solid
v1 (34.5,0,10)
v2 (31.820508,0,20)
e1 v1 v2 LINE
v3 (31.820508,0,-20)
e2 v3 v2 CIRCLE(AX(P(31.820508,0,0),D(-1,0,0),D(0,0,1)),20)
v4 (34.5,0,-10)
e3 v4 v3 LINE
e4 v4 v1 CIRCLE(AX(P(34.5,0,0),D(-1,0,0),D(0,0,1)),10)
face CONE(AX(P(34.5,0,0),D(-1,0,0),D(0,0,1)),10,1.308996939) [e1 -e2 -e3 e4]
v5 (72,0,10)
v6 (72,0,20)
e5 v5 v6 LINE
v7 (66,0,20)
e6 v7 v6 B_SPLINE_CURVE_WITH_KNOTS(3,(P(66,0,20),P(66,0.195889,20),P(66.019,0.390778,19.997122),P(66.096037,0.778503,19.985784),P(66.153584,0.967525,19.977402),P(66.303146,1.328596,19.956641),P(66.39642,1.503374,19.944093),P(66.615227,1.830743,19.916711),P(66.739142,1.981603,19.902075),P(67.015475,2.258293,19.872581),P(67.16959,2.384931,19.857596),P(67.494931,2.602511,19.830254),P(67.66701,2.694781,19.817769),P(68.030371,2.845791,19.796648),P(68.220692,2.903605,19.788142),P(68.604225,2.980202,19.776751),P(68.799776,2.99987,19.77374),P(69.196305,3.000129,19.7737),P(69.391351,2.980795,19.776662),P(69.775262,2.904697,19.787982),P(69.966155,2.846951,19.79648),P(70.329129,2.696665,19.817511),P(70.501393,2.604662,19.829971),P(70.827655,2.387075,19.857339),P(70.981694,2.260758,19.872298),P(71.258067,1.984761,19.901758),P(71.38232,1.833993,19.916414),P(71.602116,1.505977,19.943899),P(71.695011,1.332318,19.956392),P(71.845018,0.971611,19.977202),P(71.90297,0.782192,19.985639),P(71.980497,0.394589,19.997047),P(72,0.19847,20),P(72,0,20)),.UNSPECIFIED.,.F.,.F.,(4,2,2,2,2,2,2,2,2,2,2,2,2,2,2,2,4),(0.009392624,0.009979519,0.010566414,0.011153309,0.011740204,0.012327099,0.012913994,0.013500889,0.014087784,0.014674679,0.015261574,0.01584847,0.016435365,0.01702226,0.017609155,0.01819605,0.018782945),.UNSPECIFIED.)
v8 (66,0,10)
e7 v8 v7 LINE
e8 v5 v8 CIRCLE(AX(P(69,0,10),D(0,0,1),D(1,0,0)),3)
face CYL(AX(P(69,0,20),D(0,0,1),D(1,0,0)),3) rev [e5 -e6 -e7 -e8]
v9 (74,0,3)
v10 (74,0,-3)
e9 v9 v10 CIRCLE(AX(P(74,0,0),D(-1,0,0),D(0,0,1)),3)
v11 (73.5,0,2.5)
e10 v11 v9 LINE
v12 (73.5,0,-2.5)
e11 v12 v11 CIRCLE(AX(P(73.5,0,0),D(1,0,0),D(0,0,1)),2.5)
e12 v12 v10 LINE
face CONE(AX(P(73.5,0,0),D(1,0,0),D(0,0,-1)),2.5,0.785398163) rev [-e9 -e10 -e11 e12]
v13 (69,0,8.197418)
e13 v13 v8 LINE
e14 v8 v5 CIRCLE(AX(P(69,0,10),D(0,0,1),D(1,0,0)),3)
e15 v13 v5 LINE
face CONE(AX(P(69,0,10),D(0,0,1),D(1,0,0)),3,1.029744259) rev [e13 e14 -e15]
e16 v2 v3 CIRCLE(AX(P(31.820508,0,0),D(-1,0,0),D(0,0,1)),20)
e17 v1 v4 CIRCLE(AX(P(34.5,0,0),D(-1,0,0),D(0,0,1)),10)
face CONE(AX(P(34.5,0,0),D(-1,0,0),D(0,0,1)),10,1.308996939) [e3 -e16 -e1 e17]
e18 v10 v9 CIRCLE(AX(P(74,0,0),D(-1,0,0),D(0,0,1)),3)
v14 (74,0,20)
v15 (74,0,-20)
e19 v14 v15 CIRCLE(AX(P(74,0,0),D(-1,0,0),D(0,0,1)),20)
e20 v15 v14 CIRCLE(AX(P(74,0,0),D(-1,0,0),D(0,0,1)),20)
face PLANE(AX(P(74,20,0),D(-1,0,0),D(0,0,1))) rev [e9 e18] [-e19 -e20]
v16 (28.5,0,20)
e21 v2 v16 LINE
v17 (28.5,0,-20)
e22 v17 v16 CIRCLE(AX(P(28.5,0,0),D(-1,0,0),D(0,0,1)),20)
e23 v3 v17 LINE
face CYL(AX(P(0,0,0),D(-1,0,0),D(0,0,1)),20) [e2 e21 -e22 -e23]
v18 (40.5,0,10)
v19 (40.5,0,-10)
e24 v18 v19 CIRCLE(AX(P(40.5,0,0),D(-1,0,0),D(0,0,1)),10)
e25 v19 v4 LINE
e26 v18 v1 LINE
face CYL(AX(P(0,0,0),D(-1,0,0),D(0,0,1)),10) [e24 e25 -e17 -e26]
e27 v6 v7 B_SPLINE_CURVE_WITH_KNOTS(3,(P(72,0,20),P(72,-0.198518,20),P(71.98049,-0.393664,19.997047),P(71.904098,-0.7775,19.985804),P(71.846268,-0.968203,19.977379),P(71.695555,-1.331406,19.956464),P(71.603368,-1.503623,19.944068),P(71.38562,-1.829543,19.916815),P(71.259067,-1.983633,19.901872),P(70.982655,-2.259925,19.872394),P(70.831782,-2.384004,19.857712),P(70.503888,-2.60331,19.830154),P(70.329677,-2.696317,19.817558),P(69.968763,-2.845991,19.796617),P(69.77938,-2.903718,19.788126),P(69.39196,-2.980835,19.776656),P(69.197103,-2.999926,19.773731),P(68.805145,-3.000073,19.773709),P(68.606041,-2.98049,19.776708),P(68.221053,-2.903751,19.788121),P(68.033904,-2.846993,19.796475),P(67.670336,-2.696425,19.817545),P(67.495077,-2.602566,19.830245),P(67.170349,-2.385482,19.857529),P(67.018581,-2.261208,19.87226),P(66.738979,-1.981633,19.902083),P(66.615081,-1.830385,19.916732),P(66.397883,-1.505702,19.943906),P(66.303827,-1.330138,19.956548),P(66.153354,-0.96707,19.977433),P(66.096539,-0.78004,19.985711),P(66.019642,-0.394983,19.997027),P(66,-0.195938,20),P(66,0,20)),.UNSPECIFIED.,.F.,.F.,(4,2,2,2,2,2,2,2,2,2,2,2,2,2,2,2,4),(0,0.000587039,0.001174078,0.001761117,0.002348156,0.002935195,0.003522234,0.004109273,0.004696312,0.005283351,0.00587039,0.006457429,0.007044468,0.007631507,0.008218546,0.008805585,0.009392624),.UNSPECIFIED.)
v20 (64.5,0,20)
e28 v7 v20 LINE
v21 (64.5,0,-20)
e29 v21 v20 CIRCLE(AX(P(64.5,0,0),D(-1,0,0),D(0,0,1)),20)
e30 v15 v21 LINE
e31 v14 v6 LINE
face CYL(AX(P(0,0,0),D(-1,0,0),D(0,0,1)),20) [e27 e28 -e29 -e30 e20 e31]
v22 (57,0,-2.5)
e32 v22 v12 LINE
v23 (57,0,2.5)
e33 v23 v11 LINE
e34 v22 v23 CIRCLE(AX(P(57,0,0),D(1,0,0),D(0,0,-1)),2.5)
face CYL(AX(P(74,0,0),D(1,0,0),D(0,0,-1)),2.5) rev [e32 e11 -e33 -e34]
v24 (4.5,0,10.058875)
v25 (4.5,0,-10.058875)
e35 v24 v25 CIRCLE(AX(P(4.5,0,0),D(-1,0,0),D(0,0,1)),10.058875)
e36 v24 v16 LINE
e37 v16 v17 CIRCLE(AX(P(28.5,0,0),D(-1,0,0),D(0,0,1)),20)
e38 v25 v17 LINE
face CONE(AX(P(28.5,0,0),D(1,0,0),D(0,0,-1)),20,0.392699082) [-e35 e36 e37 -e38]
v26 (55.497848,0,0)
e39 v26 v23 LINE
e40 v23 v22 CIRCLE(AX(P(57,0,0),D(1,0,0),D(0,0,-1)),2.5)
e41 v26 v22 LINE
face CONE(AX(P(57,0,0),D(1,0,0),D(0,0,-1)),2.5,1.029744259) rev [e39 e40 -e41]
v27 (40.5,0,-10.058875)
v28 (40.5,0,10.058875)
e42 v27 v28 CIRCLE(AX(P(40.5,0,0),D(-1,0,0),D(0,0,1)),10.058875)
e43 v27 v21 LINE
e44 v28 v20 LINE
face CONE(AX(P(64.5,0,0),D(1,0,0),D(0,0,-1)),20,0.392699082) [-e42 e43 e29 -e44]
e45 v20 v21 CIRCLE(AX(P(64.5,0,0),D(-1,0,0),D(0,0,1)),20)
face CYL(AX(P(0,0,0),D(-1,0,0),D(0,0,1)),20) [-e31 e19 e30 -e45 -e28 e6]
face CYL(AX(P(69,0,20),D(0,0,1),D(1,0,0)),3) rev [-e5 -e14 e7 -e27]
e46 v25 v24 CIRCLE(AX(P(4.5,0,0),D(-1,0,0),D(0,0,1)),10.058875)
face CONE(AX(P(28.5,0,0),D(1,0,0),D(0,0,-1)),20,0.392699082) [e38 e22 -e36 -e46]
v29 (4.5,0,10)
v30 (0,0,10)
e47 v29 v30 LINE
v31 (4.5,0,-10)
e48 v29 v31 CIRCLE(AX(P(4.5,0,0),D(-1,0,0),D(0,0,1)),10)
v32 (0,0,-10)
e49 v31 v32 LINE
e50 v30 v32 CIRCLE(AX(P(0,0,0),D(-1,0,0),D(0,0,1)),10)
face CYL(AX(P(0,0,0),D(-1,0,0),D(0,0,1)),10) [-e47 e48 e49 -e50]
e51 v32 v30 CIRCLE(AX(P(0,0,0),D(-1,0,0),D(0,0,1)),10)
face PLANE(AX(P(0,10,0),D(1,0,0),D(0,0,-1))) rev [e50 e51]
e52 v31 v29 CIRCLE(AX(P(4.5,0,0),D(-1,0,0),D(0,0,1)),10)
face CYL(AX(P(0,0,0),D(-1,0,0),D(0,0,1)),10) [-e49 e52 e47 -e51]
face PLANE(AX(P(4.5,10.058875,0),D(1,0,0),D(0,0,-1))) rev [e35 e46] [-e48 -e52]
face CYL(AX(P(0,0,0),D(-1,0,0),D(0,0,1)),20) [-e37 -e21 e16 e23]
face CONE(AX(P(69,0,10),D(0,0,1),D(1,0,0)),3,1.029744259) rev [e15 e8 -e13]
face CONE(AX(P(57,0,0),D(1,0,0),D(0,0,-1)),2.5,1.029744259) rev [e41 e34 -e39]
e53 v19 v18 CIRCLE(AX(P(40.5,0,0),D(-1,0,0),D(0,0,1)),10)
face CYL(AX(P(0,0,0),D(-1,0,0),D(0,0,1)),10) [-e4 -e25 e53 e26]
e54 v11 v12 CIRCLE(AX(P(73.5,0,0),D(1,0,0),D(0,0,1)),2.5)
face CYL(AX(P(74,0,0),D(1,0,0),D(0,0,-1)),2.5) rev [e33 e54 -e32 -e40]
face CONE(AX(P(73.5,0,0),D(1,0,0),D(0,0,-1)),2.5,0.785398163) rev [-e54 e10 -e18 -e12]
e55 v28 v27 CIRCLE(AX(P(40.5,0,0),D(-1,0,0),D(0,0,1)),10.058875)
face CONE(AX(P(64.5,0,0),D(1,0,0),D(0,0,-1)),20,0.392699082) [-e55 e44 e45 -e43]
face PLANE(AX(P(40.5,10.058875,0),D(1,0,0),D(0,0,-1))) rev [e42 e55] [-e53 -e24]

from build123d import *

# Parameters (mm, degrees)
HOLE_WIZARD_M6_1_D        = 5
HOLE_WIZARD_M6_1_DEPTH    = 17
HOLE_WIZARD_M6_1_TIP      = 1.502151548
CHAMFER_1_SIZE            = 0.5
HOLE_WIZARD_6_0_6_1_D     = 6
HOLE_WIZARD_6_0_6_1_DEPTH = 10
HOLE_WIZARD_6_0_6_1_TIP   = 1.802581857


with BuildPart() as part:
    # 草图1 → 旋转1 (revolve)
    with BuildSketch(Plane.XY, mode=Mode.PRIVATE) as revolve_1_sk:
        Polygon((4.5, 10), (0, 10), (0, 0), (74, 0), (74, 20), (64.5, 20), (40.5, 10.058874503), (40.5, 10), (34.5, 10), (31.820508076, 20), (28.5, 20), (4.5, 10.058874503), align=None)
    revolve(revolve_1_sk.sketch.rotate(Axis((0, 0, 0), (1, 0, 0)), 90), axis=Axis((0, 0, 0), (1, 0, 0)))

    # M6 螺纹孔1
    with Locations(Plane(origin=(74, 0, 0), x_dir=(0, 0, -1), z_dir=(1, 0, 0))):
        with Locations((0, 0)):
            Hole(HOLE_WIZARD_M6_1_D / 2, depth=HOLE_WIZARD_M6_1_DEPTH)
            with Locations((0, 0, -(HOLE_WIZARD_M6_1_DEPTH + HOLE_WIZARD_M6_1_TIP / 2))):  # 118° drill point
                Cone(0, HOLE_WIZARD_M6_1_D / 2, HOLE_WIZARD_M6_1_TIP, mode=Mode.SUBTRACT)

    # 倒角1
    chamfer_1_edges = [part.edges().sort_by_distance(p)[0] for p in [
        (74, 0, -2.5),
    ]]
    chamfer(chamfer_1_edges, length=CHAMFER_1_SIZE)

    # Ø6.0 (6) 直径孔1
    with Locations(Plane(origin=(69, 0, 20), x_dir=(1, 0, 0), z_dir=(0, 0, 1))):
        with Locations((0, 0)):
            Hole(HOLE_WIZARD_6_0_6_1_D / 2, depth=HOLE_WIZARD_6_0_6_1_DEPTH)
            with Locations((0, 0, -(HOLE_WIZARD_6_0_6_1_DEPTH + HOLE_WIZARD_6_0_6_1_TIP / 2))):  # 118° drill point
                Cone(0, HOLE_WIZARD_6_0_6_1_D / 2, HOLE_WIZARD_6_0_6_1_TIP, mode=Mode.SUBTRACT)


solid = part.part
